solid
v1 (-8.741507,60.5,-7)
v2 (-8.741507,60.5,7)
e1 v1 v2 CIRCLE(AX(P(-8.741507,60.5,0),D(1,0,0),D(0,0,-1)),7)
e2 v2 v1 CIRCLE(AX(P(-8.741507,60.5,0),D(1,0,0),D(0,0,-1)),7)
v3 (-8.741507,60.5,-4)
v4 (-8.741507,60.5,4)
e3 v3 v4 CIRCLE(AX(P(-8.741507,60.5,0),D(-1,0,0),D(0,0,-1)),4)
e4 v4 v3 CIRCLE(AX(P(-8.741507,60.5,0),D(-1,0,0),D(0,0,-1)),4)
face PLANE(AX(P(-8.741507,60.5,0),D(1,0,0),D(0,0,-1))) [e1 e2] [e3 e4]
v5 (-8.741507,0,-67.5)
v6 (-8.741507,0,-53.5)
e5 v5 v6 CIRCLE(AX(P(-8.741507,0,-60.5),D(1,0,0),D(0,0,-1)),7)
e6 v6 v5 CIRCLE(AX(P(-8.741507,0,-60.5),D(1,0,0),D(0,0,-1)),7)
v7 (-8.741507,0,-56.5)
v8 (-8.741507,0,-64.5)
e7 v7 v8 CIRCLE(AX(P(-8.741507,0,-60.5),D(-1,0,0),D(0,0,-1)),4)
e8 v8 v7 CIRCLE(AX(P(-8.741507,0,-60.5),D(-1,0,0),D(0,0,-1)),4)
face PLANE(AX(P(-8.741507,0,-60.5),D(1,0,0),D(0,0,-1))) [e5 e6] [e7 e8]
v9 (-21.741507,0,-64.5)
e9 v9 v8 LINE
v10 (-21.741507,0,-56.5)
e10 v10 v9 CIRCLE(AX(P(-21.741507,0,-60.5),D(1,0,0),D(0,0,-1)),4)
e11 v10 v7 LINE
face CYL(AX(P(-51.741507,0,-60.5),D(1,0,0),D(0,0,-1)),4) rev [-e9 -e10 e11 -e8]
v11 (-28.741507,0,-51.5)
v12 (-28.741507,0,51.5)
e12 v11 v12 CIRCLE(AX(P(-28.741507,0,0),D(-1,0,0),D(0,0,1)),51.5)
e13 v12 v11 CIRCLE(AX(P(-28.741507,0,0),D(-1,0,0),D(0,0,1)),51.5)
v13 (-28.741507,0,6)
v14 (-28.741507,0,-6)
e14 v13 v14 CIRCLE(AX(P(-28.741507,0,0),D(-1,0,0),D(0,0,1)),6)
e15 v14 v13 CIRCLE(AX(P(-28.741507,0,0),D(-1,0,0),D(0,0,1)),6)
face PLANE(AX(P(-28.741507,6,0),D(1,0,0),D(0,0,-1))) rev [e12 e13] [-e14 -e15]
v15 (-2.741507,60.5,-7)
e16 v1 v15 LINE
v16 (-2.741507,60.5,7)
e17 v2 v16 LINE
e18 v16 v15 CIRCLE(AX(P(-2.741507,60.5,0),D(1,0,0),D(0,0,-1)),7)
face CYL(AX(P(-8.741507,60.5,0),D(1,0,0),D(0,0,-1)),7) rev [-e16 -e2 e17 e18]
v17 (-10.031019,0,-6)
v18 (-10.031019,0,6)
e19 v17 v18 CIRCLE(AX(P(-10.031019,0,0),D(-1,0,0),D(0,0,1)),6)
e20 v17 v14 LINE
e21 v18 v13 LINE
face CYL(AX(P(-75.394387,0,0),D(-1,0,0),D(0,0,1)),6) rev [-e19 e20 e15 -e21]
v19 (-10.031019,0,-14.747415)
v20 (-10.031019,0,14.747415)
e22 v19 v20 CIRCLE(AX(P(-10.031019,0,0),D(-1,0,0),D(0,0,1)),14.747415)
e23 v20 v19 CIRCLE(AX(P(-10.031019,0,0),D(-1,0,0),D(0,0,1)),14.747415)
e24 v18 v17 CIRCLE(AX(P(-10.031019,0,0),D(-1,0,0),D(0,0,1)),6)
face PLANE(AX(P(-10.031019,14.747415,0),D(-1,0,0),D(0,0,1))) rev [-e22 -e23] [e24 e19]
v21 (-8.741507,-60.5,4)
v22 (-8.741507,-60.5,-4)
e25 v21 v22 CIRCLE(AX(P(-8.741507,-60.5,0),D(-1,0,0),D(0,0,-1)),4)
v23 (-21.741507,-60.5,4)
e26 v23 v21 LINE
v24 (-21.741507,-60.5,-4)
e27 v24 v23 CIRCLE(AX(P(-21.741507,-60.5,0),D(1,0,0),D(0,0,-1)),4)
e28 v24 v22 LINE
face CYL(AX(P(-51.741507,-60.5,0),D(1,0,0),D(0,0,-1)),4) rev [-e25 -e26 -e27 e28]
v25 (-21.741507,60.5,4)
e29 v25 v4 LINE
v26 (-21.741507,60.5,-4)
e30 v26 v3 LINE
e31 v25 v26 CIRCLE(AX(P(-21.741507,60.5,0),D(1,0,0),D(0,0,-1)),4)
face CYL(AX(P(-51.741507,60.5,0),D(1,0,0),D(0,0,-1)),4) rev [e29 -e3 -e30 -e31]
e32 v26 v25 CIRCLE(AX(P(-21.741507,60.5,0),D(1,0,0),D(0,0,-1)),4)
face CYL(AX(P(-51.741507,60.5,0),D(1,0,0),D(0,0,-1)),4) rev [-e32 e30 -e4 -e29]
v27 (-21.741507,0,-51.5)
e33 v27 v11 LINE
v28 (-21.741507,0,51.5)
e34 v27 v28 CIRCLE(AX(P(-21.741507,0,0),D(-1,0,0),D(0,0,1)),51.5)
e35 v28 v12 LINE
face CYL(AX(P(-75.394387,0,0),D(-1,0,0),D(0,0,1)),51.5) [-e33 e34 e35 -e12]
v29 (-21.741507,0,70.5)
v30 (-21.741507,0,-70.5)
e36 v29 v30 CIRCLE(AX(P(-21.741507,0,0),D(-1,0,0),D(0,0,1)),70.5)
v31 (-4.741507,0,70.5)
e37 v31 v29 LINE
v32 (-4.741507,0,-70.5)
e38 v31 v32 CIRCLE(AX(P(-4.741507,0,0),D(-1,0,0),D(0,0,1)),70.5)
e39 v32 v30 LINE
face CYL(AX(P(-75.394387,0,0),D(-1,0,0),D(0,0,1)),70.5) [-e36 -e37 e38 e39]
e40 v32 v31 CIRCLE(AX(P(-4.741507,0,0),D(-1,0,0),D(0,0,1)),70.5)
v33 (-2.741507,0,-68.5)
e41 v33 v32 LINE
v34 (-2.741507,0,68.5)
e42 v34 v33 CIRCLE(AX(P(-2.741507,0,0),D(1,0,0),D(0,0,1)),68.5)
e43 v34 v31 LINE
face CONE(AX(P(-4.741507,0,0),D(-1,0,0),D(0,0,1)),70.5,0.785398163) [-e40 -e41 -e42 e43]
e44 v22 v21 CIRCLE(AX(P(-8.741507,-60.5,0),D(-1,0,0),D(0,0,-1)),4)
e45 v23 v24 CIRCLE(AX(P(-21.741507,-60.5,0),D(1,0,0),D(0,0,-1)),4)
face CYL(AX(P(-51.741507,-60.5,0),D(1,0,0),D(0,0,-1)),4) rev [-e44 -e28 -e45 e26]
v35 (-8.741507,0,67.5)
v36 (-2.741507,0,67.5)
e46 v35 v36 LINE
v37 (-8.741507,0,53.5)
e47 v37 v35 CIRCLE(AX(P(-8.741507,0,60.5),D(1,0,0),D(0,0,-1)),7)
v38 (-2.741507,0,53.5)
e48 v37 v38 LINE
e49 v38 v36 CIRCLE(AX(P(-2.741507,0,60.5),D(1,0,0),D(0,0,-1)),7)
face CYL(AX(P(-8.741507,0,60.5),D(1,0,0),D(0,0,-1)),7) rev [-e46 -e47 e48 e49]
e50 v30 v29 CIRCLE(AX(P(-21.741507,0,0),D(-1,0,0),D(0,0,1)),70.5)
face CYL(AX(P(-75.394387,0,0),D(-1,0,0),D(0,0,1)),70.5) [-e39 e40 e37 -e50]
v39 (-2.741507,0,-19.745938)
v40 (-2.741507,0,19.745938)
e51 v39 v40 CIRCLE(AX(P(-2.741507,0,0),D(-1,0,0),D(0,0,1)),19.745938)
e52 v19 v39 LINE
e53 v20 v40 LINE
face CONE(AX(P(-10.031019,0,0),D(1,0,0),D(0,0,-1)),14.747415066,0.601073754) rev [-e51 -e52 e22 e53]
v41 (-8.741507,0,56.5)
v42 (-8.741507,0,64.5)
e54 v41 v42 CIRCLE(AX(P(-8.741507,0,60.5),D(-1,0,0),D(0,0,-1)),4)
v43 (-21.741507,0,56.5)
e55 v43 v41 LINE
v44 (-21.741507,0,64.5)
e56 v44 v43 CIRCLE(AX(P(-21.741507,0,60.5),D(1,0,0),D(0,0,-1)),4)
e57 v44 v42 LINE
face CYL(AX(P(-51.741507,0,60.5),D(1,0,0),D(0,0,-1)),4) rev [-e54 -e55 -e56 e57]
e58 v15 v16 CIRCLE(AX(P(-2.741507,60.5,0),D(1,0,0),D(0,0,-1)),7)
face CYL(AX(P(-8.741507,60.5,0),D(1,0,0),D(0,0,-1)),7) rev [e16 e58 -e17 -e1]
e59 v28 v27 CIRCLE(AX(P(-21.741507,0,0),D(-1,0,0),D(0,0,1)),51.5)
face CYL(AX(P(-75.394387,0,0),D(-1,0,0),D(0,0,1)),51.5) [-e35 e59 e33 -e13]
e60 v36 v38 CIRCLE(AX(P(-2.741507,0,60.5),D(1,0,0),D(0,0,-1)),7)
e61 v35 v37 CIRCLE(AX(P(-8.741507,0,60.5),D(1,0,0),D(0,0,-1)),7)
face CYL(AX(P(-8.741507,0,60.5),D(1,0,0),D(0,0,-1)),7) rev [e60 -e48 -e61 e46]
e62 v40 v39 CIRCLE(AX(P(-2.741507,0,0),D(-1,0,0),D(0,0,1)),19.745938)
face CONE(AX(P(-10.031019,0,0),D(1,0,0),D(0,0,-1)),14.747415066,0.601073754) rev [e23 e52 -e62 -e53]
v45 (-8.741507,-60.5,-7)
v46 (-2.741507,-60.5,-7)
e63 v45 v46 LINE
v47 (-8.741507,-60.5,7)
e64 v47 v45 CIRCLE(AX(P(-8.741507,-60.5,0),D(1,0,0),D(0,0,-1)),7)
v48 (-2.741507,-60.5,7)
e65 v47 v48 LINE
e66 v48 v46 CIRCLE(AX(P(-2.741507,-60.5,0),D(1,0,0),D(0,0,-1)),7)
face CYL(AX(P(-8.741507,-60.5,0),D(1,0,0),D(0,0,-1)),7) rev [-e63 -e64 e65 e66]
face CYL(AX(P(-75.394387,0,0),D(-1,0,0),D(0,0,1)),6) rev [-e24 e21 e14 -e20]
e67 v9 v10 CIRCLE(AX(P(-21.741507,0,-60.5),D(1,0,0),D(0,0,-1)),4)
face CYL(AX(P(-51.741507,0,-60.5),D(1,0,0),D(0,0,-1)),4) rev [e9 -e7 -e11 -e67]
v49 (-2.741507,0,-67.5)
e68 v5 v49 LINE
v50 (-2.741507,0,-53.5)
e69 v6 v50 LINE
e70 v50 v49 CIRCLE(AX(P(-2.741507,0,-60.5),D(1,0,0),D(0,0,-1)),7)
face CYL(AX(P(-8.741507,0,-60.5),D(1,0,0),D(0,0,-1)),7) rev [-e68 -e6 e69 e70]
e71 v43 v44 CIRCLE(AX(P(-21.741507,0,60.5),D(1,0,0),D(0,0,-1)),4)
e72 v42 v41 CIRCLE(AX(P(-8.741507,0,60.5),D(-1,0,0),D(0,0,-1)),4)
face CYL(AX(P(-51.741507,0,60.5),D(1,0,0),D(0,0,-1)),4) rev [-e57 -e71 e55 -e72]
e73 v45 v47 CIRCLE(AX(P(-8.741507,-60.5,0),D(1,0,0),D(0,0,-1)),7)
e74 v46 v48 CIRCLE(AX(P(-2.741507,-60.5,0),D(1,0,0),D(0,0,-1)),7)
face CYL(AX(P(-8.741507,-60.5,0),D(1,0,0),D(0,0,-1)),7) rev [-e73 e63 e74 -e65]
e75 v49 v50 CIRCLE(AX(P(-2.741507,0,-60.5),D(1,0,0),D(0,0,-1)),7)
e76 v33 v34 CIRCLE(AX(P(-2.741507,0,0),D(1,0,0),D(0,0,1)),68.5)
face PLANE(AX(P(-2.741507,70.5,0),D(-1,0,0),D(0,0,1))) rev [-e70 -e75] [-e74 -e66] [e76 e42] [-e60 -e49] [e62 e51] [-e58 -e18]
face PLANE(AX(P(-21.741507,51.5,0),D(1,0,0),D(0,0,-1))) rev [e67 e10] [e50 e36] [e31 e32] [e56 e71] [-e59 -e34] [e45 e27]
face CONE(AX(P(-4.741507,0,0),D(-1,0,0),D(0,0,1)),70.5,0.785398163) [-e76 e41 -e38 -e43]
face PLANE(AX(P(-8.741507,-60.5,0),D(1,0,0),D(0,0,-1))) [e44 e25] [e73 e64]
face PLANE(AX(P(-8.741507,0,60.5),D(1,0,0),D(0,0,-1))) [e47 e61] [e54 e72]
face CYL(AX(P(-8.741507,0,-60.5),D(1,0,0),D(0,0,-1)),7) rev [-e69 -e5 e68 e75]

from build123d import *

# Parameters (mm, degrees)
CHAMFER1_SIZE      = 2
SKETCH2_R          = 4
CUT_EXTRUDE1_DEPTH = 49
SKETCH3_R          = 7
CUT_EXTRUDE2_DEPTH = 6


with BuildPart() as part:
    # Sketch1 → Revolve1 (revolve)
    with BuildSketch(Plane.XY, mode=Mode.PRIVATE) as revolve1_sk:
        Polygon((-28.741506647, 6), (-28.741506647, 51.5), (-21.741506647, 51.5), (-21.741506647, 70.5), (-2.741506647, 70.5), (-2.741506647, 19.745937962), (-10.031019202, 14.747415066), (-10.031019202, 6), align=None)
    revolve(revolve1_sk.sketch.rotate(Axis((-75.394387001, 0, 0), (1, 0, 0)), 90), axis=Axis((-75.394387001, 0, 0), (1, 0, 0)))

    # Chamfer1
    chamfer1_edges = [part.edges().sort_by_distance(p)[0] for p in [
        (-2.741506647, 0, -70.5),
    ]]
    chamfer(chamfer1_edges, length=CHAMFER1_SIZE)

    # Sketch2 → Cut-Extrude1 (cut)
    with BuildSketch(Plane(origin=(-2.741506647, 0, 0), x_dir=(0, 0, -1), z_dir=(1, 0, 0))):
        with Locations((0, -60.5)):
            Circle(SKETCH2_R)
        with Locations((-60.5, 0)):
            Circle(SKETCH2_R)
        with Locations((0, 60.5)):
            Circle(SKETCH2_R)
        with Locations((60.5, 0)):
            Circle(SKETCH2_R)
    extrude(amount=-CUT_EXTRUDE1_DEPTH, mode=Mode.SUBTRACT)

    # Sketch3 → Cut-Extrude2 (cut)
    with BuildSketch(Plane(origin=(-2.741506647, 0, 0), x_dir=(0, 0, -1), z_dir=(1, 0, 0))):
        with Locations((-60.5, 0)):
            Circle(SKETCH3_R)
        with Locations((0, 60.5)):
            Circle(SKETCH3_R)
        with Locations((60.5, 0)):
            Circle(SKETCH3_R)
        with Locations((0, -60.5)):
            Circle(SKETCH3_R)
    extrude(amount=-CUT_EXTRUDE2_DEPTH, mode=Mode.SUBTRACT)


solid = part.part
